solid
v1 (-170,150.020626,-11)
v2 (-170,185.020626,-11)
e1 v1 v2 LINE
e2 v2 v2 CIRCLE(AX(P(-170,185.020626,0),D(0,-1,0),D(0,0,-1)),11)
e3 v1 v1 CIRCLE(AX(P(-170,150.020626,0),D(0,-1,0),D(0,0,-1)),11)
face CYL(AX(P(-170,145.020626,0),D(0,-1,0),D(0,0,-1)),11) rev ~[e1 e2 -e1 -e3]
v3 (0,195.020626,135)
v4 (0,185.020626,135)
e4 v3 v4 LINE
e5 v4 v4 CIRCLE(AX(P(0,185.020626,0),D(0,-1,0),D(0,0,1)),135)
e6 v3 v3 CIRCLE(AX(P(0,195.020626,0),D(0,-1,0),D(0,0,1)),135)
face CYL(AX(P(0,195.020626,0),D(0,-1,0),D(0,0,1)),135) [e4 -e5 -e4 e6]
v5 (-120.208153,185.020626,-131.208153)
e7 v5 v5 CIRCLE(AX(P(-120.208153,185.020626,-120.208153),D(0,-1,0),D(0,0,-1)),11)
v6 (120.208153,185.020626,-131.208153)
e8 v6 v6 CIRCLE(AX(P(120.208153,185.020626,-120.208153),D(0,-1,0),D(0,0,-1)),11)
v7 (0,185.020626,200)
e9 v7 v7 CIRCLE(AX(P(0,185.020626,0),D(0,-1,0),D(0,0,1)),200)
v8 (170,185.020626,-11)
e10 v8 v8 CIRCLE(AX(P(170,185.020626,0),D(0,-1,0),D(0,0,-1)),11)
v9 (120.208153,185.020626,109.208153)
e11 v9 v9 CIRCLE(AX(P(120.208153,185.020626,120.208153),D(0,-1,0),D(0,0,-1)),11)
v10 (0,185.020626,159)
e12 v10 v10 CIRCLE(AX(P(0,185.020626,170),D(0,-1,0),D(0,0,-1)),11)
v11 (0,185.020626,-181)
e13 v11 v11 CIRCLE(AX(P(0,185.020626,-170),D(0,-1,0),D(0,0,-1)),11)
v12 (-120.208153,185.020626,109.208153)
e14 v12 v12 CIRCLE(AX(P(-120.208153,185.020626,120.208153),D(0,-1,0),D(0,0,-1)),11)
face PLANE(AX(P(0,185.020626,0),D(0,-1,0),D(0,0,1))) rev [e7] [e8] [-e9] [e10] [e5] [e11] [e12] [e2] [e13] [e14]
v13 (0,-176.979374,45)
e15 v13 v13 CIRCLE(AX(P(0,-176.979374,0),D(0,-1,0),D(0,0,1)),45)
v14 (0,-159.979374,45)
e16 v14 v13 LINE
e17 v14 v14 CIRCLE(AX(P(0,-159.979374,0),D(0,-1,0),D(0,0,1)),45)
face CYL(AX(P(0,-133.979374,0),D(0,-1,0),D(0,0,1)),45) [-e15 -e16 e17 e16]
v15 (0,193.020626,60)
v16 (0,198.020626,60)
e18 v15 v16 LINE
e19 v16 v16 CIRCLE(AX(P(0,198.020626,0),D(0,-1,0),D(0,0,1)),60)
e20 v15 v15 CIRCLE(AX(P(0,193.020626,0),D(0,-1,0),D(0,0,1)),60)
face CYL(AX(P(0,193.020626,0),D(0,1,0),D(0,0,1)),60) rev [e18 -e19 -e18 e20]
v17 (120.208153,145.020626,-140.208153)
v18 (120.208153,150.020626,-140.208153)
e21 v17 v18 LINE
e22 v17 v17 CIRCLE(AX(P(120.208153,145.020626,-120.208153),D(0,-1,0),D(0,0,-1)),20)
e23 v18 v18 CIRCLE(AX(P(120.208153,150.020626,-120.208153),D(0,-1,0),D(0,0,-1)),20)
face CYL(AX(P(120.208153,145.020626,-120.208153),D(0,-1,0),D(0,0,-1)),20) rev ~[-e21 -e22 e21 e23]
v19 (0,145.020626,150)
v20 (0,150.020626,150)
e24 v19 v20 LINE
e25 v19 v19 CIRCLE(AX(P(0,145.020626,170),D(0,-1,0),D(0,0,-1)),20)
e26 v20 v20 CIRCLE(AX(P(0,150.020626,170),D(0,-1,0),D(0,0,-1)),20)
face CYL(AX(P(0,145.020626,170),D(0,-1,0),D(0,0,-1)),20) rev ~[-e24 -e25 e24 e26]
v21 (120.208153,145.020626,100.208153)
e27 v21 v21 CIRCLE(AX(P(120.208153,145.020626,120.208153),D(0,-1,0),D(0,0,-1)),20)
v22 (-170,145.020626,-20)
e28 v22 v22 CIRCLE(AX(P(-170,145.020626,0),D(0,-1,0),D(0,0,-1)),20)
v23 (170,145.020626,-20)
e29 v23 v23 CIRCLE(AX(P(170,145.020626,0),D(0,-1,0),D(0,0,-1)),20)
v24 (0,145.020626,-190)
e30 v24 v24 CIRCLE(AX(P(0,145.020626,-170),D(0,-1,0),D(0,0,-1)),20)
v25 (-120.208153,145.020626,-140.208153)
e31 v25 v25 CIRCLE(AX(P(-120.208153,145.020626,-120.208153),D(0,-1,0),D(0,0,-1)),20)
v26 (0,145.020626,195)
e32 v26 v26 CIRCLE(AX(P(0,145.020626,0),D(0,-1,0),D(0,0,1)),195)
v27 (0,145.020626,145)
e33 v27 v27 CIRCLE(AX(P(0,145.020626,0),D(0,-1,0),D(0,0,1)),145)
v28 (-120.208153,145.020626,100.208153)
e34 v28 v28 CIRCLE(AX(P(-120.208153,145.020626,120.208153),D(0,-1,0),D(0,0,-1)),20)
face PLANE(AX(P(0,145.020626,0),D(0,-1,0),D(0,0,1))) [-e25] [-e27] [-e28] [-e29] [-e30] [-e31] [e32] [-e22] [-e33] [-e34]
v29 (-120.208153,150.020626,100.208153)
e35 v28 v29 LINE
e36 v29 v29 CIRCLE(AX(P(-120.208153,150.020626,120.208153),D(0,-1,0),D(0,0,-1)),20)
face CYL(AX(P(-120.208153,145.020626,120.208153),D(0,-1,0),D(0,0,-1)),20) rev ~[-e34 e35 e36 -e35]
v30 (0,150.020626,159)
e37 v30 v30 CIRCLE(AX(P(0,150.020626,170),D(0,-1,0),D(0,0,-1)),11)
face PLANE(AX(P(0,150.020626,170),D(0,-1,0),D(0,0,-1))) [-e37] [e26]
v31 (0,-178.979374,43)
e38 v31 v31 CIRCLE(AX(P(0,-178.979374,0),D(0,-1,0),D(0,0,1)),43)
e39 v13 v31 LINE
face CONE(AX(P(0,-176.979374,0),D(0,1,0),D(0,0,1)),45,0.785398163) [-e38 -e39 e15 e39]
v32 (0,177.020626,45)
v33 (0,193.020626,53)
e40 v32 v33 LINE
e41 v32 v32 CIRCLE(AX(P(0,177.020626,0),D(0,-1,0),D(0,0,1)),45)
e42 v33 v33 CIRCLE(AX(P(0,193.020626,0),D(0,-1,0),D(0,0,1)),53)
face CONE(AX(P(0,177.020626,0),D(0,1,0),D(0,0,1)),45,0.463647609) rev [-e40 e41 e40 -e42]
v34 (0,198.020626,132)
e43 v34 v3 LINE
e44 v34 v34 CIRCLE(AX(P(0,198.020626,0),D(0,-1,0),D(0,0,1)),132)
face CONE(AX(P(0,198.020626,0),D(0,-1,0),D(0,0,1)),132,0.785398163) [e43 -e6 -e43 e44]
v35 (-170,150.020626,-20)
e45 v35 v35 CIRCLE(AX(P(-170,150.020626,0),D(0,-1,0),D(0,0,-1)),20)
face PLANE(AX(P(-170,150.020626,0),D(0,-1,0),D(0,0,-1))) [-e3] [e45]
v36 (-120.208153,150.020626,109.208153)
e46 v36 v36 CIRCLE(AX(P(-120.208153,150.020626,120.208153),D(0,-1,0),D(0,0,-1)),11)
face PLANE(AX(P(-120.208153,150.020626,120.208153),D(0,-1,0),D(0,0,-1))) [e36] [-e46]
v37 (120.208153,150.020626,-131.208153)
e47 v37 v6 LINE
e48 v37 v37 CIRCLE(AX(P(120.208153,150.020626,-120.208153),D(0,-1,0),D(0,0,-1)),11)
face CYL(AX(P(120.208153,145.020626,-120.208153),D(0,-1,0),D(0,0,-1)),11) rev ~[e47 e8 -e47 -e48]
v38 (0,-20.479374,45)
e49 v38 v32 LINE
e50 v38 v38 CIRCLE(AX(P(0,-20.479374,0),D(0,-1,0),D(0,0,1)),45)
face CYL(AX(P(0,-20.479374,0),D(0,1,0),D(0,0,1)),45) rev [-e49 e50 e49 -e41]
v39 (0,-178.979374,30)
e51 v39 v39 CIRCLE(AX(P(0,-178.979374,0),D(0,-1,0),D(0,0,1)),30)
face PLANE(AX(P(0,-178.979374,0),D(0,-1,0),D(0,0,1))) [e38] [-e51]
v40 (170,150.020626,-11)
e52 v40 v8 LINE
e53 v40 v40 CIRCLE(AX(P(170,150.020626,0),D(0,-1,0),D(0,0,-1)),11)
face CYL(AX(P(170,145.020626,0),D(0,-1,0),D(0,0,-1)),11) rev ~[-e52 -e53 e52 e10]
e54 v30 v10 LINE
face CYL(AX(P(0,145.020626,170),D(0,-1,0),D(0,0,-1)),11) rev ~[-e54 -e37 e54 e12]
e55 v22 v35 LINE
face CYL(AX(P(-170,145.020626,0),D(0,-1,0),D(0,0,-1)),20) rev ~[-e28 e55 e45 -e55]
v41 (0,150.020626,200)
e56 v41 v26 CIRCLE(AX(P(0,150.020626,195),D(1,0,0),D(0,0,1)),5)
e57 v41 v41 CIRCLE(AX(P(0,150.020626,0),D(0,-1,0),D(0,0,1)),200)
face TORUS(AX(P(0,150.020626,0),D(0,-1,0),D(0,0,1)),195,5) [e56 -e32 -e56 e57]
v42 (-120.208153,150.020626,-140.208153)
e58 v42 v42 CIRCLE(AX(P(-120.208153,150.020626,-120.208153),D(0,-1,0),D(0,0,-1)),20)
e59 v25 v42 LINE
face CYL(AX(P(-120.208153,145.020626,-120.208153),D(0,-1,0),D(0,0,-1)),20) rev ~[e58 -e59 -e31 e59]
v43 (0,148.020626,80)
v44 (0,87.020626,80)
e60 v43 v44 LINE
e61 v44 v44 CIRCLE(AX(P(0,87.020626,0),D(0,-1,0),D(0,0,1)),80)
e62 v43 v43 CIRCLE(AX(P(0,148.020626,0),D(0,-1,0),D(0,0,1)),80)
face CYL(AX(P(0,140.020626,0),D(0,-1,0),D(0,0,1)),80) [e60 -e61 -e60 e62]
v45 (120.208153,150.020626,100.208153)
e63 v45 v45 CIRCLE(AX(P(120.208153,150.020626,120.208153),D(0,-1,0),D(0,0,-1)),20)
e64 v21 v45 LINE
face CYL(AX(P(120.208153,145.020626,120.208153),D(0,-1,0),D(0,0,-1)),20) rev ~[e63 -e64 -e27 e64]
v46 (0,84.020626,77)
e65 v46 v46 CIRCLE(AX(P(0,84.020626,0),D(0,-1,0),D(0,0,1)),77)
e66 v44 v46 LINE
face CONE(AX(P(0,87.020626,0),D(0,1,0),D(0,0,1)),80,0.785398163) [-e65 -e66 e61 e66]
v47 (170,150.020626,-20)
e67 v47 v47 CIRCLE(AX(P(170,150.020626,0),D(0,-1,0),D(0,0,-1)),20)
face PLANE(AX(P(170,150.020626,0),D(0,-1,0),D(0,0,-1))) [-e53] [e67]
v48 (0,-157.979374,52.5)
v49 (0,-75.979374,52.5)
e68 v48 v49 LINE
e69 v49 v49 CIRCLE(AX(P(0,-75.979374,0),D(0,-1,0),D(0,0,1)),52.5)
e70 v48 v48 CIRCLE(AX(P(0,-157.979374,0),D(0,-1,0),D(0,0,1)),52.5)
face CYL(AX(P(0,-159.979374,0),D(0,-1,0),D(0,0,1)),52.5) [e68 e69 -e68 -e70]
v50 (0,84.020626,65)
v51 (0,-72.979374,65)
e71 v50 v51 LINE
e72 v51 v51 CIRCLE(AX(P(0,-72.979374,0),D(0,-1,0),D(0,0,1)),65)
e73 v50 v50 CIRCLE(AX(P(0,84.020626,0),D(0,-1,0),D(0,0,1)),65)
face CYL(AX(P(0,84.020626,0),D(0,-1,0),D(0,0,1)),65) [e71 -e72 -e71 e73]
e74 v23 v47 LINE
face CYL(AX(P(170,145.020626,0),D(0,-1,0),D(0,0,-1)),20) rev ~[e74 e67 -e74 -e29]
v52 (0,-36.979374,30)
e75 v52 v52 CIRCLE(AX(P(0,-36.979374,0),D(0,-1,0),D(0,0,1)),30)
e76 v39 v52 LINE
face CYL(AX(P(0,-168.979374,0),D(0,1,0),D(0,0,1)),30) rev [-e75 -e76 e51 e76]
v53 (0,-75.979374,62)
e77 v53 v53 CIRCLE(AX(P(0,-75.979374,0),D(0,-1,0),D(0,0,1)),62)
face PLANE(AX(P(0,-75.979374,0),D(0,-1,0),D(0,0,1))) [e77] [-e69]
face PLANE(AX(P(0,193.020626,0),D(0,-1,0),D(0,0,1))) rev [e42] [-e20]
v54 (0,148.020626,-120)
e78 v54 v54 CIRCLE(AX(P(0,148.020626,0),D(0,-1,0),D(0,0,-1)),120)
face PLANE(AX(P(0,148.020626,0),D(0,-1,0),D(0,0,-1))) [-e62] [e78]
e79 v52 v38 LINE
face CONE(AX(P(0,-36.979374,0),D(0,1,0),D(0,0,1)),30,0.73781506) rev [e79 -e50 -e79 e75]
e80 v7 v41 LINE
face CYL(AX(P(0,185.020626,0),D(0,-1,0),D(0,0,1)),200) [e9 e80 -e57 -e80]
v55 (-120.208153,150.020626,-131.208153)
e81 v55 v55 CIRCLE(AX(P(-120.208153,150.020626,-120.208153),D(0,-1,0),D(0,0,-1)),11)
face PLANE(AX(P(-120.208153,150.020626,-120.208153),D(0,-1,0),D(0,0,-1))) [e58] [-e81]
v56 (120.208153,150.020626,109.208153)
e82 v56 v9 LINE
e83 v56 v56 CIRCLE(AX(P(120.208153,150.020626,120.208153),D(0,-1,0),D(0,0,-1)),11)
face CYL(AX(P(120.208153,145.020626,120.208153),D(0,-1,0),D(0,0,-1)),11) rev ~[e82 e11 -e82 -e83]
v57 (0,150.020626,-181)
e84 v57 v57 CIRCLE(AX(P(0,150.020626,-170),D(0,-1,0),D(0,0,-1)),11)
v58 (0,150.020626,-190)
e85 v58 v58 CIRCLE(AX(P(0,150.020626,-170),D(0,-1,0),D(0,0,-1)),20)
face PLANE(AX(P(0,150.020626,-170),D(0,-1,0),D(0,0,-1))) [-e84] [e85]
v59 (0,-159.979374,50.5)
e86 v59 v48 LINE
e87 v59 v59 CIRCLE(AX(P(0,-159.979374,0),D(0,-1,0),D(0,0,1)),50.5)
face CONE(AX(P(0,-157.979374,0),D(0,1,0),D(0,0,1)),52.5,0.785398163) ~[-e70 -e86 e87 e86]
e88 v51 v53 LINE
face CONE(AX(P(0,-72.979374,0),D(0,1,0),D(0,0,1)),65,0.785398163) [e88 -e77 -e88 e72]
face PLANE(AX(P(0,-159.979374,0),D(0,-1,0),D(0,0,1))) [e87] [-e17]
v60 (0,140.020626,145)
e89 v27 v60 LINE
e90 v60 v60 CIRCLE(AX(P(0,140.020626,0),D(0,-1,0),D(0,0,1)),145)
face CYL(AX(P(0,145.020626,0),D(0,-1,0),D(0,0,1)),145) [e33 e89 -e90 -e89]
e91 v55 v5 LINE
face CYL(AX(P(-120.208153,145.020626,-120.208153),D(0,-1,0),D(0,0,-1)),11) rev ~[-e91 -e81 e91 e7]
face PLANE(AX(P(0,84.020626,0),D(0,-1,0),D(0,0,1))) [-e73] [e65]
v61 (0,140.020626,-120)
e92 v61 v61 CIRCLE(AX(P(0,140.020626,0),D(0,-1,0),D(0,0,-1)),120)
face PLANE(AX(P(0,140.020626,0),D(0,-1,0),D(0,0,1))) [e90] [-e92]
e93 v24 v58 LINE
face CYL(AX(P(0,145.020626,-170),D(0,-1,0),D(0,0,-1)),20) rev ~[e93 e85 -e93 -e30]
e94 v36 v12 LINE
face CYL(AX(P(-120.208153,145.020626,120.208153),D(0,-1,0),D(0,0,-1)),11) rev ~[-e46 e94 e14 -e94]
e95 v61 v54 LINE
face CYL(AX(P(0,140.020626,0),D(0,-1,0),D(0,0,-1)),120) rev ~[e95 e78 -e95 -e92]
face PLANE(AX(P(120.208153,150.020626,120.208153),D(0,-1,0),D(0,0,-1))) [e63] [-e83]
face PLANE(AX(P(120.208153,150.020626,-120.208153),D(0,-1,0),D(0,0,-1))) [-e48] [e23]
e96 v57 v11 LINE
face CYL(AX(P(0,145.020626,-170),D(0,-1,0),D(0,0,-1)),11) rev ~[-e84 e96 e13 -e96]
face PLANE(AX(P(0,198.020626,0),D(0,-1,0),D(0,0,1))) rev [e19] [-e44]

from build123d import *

# Parameters (mm, degrees)
SKETCH_2_R          = 20
CUT_EXTRUDE_1_DEPTH = 5
CUT_EXTRUDE_2_REACH = 424.606
SKETCH_3_R          = 11
SKETCH_5_R          = 120
SKETCH_5_R_2        = 80
CUT_EXTRUDE_3_DEPTH = 8
EXTRUDE_START       = 26
SKETCH_6_R          = 52.5
SKETCH_6_R_2        = 45
EXTRUDE_1_DEPTH     = 26
SKETCH_7_R          = 45
SKETCH_7_R_2        = 30
EXTRUDE_2_DEPTH     = 10
CHAMFER_1_SIZE      = 2
CHAMFER_2_SIZE      = 2


with BuildPart() as part:
    # 草图1 → 旋转1 (revolve)
    with BuildSketch(Plane.XY, mode=Mode.PRIVATE) as revolve_1_sk:
        with BuildLine():
            Line((60, 198.020625577), (132, 198.020625577))
            Line((132, 198.020625577), (135, 195.020625577))
            Line((135, 195.020625577), (135, 185.020625577))
            Line((135, 185.020625577), (200, 185.020625577))
            Line((200, 185.020625577), (200, 150.020625577))
            ThreePointArc((200, 150.020625577), (198.535533906, 146.485091671), (195, 145.020625577))
            Line((195, 145.020625577), (145, 145.020625577))
            Line((145, 145.020625577), (145, 140.020625577))
            Line((145, 140.020625577), (80, 140.020625577))
            Line((80, 140.020625577), (80, 87.020625577))
            Line((80, 87.020625577), (77, 84.020625577))
            Line((77, 84.020625577), (65, 84.020625577))
            Line((65, 84.020625577), (65, -72.979374423))
            Line((65, -72.979374423), (62, -75.979374423))
            Line((62, -75.979374423), (52.5, -75.979374423))
            Line((52.5, -75.979374423), (52.5, -131.979374423))
            Line((52.5, -131.979374423), (52.5, -133.979374423))
            Line((52.5, -133.979374423), (50.5, -133.979374423))
            Line((50.5, -133.979374423), (45, -133.979374423))
            Line((45, -133.979374423), (45, -167.979374423))
            Line((45, -167.979374423), (45, -168.979374423))
            Line((45, -168.979374423), (44, -168.979374423))
            Line((44, -168.979374423), (30, -168.979374423))
            Line((30, -168.979374423), (30, -36.979374423))
            Line((30, -36.979374423), (45, -20.479374423))
            Line((45, -20.479374423), (45, 177.020625577))
            Line((45, 177.020625577), (53, 193.020625577))
            Line((53, 193.020625577), (60, 193.020625577))
            Line((60, 193.020625577), (60, 198.020625577))
        make_face()
    revolve(revolve_1_sk.sketch.rotate(Axis((0, 246.142362889, 0), (0, -1, 0)), 90), axis=Axis((0, 246.142362889, 0), (0, -1, 0)))

    # 草图2 → 切除-拉伸1 (cut)
    with BuildSketch(Plane.XZ.offset(-145.020625577)):
        with Locations(Location((-120.208152802, 120.208152802, 0), (0, 0, 270))):
            Circle(SKETCH_2_R)
        with Locations(Location((-170, 0, 0), (0, 0, 270))):
            Circle(SKETCH_2_R)
        with Locations(Location((0, 170, 0), (0, 0, 270))):
            Circle(SKETCH_2_R)
        with Locations(Location((120.208152802, 120.208152802, 0), (0, 0, 270))):
            Circle(SKETCH_2_R)
        with Locations(Location((170, 0, 0), (0, 0, 270))):
            Circle(SKETCH_2_R)
        with Locations(Location((120.208152802, -120.208152802, 0), (0, 0, 270))):
            Circle(SKETCH_2_R)
        with Locations(Location((0, -170, 0), (0, 0, 270))):
            Circle(SKETCH_2_R)
        with Locations(Location((-120.208152802, -120.208152802, 0), (0, 0, 270))):
            Circle(SKETCH_2_R)
    extrude(amount=-CUT_EXTRUDE_1_DEPTH, mode=Mode.SUBTRACT)

    # 草图3 → 切除-拉伸2 (cut, up to next)
    with BuildSketch(Plane.XZ.offset(-145.020625577), mode=Mode.PRIVATE) as cut_extrude_2_sk1:
        with Locations(Location((-170, 0, 0), (0, 0, 270))):
            Circle(SKETCH_3_R)
    cut_extrude_2_tool1 = extrude(cut_extrude_2_sk1.sketch, amount=-CUT_EXTRUDE_2_REACH, mode=Mode.PRIVATE) & part.part
    # 草图3 → 切除-拉伸2 (cut, up to next)
    with BuildSketch(Plane.XZ.offset(-145.020625577), mode=Mode.PRIVATE) as cut_extrude_2_sk2:
        with Locations(Location((-120.208152802, 120.208152802, 0), (0, 0, 270))):
            Circle(SKETCH_3_R)
    cut_extrude_2_tool2 = extrude(cut_extrude_2_sk2.sketch, amount=-CUT_EXTRUDE_2_REACH, mode=Mode.PRIVATE) & part.part
    # 草图3 → 切除-拉伸2 (cut, up to next)
    with BuildSketch(Plane.XZ.offset(-145.020625577), mode=Mode.PRIVATE) as cut_extrude_2_sk3:
        with Locations(Location((0, 170, 0), (0, 0, 270))):
            Circle(SKETCH_3_R)
    cut_extrude_2_tool3 = extrude(cut_extrude_2_sk3.sketch, amount=-CUT_EXTRUDE_2_REACH, mode=Mode.PRIVATE) & part.part
    # 草图3 → 切除-拉伸2 (cut, up to next)
    with BuildSketch(Plane.XZ.offset(-145.020625577), mode=Mode.PRIVATE) as cut_extrude_2_sk4:
        with Locations(Location((120.208152802, 120.208152802, 0), (0, 0, 270))):
            Circle(SKETCH_3_R)
    cut_extrude_2_tool4 = extrude(cut_extrude_2_sk4.sketch, amount=-CUT_EXTRUDE_2_REACH, mode=Mode.PRIVATE) & part.part
    # 草图3 → 切除-拉伸2 (cut, up to next)
    with BuildSketch(Plane.XZ.offset(-145.020625577), mode=Mode.PRIVATE) as cut_extrude_2_sk5:
        with Locations(Location((170, 0, 0), (0, 0, 270))):
            Circle(SKETCH_3_R)
    cut_extrude_2_tool5 = extrude(cut_extrude_2_sk5.sketch, amount=-CUT_EXTRUDE_2_REACH, mode=Mode.PRIVATE) & part.part
    # 草图3 → 切除-拉伸2 (cut, up to next)
    with BuildSketch(Plane.XZ.offset(-145.020625577), mode=Mode.PRIVATE) as cut_extrude_2_sk6:
        with Locations(Location((120.208152802, -120.208152802, 0), (0, 0, 270))):
            Circle(SKETCH_3_R)
    cut_extrude_2_tool6 = extrude(cut_extrude_2_sk6.sketch, amount=-CUT_EXTRUDE_2_REACH, mode=Mode.PRIVATE) & part.part
    # 草图3 → 切除-拉伸2 (cut, up to next)
    with BuildSketch(Plane.XZ.offset(-145.020625577), mode=Mode.PRIVATE) as cut_extrude_2_sk7:
        with Locations(Location((0, -170, 0), (0, 0, 270))):
            Circle(SKETCH_3_R)
    cut_extrude_2_tool7 = extrude(cut_extrude_2_sk7.sketch, amount=-CUT_EXTRUDE_2_REACH, mode=Mode.PRIVATE) & part.part
    # 草图3 → 切除-拉伸2 (cut, up to next)
    with BuildSketch(Plane.XZ.offset(-145.020625577), mode=Mode.PRIVATE) as cut_extrude_2_sk8:
        with Locations(Location((-120.208152802, -120.208152802, 0), (0, 0, 270))):
            Circle(SKETCH_3_R)
    cut_extrude_2_tool8 = extrude(cut_extrude_2_sk8.sketch, amount=-CUT_EXTRUDE_2_REACH, mode=Mode.PRIVATE) & part.part
    add(cut_extrude_2_tool1.solids().sort_by_distance((-170, 145.020626, 0))[0], mode=Mode.SUBTRACT)
    add(cut_extrude_2_tool2.solids().sort_by_distance((-120.208153, 145.020626, 120.208153))[0], mode=Mode.SUBTRACT)
    add(cut_extrude_2_tool3.solids().sort_by_distance((0, 145.020626, 170))[0], mode=Mode.SUBTRACT)
    add(cut_extrude_2_tool4.solids().sort_by_distance((120.208153, 145.020626, 120.208153))[0], mode=Mode.SUBTRACT)
    add(cut_extrude_2_tool5.solids().sort_by_distance((170, 145.020626, 0))[0], mode=Mode.SUBTRACT)
    add(cut_extrude_2_tool6.solids().sort_by_distance((120.208153, 145.020626, -120.208153))[0], mode=Mode.SUBTRACT)
    add(cut_extrude_2_tool7.solids().sort_by_distance((0, 145.020626, -170))[0], mode=Mode.SUBTRACT)
    add(cut_extrude_2_tool8.solids().sort_by_distance((-120.208153, 145.020626, -120.208153))[0], mode=Mode.SUBTRACT)

    # 草图5 → 切除-拉伸3 (cut)
    with BuildSketch(Plane.XZ.offset(-140.020625577)):
        with Locations(Location((0, 0, 0), (0, 0, 270))):
            Circle(SKETCH_5_R)
        with Locations(Location((0, 0, 0), (0, 0, 90))):
            Circle(SKETCH_5_R_2, mode=Mode.SUBTRACT)
    extrude(amount=-CUT_EXTRUDE_3_DEPTH, mode=Mode.SUBTRACT)

    # 草图6 → 凸台-拉伸1 (add)
    with BuildSketch(Plane.XZ.offset(133.979374423).offset(EXTRUDE_START)):
        with Locations(Location((0, 0, 0), (0, 0, 90))):
            Circle(SKETCH_6_R)
        with Locations(Location((0, 0, 0), (0, 0, 90))):
            Circle(SKETCH_6_R_2, mode=Mode.SUBTRACT)
    extrude(amount=-EXTRUDE_1_DEPTH)

    # 草图7 → 凸台-拉伸2 (add)
    with BuildSketch(Plane.XZ.offset(168.979374423)):
        with Locations(Location((0, 0, 0), (0, 0, 90))):
            Circle(SKETCH_7_R)
        with Locations(Location((0, 0, 0), (0, 0, 90))):
            Circle(SKETCH_7_R_2, mode=Mode.SUBTRACT)
    extrude(amount=EXTRUDE_2_DEPTH)

    # 倒角1
    chamfer_1_edges = [part.edges().sort_by_distance(p)[0] for p in [
        (0, -159.979374423, -52.5),
    ]]
    chamfer(chamfer_1_edges, length=CHAMFER_1_SIZE)

    # 倒角2
    chamfer_2_edges = [part.edges().sort_by_distance(p)[0] for p in [
        (0, -178.979374423, -45),
    ]]
    chamfer(chamfer_2_edges, length=CHAMFER_2_SIZE)


solid = part.part
